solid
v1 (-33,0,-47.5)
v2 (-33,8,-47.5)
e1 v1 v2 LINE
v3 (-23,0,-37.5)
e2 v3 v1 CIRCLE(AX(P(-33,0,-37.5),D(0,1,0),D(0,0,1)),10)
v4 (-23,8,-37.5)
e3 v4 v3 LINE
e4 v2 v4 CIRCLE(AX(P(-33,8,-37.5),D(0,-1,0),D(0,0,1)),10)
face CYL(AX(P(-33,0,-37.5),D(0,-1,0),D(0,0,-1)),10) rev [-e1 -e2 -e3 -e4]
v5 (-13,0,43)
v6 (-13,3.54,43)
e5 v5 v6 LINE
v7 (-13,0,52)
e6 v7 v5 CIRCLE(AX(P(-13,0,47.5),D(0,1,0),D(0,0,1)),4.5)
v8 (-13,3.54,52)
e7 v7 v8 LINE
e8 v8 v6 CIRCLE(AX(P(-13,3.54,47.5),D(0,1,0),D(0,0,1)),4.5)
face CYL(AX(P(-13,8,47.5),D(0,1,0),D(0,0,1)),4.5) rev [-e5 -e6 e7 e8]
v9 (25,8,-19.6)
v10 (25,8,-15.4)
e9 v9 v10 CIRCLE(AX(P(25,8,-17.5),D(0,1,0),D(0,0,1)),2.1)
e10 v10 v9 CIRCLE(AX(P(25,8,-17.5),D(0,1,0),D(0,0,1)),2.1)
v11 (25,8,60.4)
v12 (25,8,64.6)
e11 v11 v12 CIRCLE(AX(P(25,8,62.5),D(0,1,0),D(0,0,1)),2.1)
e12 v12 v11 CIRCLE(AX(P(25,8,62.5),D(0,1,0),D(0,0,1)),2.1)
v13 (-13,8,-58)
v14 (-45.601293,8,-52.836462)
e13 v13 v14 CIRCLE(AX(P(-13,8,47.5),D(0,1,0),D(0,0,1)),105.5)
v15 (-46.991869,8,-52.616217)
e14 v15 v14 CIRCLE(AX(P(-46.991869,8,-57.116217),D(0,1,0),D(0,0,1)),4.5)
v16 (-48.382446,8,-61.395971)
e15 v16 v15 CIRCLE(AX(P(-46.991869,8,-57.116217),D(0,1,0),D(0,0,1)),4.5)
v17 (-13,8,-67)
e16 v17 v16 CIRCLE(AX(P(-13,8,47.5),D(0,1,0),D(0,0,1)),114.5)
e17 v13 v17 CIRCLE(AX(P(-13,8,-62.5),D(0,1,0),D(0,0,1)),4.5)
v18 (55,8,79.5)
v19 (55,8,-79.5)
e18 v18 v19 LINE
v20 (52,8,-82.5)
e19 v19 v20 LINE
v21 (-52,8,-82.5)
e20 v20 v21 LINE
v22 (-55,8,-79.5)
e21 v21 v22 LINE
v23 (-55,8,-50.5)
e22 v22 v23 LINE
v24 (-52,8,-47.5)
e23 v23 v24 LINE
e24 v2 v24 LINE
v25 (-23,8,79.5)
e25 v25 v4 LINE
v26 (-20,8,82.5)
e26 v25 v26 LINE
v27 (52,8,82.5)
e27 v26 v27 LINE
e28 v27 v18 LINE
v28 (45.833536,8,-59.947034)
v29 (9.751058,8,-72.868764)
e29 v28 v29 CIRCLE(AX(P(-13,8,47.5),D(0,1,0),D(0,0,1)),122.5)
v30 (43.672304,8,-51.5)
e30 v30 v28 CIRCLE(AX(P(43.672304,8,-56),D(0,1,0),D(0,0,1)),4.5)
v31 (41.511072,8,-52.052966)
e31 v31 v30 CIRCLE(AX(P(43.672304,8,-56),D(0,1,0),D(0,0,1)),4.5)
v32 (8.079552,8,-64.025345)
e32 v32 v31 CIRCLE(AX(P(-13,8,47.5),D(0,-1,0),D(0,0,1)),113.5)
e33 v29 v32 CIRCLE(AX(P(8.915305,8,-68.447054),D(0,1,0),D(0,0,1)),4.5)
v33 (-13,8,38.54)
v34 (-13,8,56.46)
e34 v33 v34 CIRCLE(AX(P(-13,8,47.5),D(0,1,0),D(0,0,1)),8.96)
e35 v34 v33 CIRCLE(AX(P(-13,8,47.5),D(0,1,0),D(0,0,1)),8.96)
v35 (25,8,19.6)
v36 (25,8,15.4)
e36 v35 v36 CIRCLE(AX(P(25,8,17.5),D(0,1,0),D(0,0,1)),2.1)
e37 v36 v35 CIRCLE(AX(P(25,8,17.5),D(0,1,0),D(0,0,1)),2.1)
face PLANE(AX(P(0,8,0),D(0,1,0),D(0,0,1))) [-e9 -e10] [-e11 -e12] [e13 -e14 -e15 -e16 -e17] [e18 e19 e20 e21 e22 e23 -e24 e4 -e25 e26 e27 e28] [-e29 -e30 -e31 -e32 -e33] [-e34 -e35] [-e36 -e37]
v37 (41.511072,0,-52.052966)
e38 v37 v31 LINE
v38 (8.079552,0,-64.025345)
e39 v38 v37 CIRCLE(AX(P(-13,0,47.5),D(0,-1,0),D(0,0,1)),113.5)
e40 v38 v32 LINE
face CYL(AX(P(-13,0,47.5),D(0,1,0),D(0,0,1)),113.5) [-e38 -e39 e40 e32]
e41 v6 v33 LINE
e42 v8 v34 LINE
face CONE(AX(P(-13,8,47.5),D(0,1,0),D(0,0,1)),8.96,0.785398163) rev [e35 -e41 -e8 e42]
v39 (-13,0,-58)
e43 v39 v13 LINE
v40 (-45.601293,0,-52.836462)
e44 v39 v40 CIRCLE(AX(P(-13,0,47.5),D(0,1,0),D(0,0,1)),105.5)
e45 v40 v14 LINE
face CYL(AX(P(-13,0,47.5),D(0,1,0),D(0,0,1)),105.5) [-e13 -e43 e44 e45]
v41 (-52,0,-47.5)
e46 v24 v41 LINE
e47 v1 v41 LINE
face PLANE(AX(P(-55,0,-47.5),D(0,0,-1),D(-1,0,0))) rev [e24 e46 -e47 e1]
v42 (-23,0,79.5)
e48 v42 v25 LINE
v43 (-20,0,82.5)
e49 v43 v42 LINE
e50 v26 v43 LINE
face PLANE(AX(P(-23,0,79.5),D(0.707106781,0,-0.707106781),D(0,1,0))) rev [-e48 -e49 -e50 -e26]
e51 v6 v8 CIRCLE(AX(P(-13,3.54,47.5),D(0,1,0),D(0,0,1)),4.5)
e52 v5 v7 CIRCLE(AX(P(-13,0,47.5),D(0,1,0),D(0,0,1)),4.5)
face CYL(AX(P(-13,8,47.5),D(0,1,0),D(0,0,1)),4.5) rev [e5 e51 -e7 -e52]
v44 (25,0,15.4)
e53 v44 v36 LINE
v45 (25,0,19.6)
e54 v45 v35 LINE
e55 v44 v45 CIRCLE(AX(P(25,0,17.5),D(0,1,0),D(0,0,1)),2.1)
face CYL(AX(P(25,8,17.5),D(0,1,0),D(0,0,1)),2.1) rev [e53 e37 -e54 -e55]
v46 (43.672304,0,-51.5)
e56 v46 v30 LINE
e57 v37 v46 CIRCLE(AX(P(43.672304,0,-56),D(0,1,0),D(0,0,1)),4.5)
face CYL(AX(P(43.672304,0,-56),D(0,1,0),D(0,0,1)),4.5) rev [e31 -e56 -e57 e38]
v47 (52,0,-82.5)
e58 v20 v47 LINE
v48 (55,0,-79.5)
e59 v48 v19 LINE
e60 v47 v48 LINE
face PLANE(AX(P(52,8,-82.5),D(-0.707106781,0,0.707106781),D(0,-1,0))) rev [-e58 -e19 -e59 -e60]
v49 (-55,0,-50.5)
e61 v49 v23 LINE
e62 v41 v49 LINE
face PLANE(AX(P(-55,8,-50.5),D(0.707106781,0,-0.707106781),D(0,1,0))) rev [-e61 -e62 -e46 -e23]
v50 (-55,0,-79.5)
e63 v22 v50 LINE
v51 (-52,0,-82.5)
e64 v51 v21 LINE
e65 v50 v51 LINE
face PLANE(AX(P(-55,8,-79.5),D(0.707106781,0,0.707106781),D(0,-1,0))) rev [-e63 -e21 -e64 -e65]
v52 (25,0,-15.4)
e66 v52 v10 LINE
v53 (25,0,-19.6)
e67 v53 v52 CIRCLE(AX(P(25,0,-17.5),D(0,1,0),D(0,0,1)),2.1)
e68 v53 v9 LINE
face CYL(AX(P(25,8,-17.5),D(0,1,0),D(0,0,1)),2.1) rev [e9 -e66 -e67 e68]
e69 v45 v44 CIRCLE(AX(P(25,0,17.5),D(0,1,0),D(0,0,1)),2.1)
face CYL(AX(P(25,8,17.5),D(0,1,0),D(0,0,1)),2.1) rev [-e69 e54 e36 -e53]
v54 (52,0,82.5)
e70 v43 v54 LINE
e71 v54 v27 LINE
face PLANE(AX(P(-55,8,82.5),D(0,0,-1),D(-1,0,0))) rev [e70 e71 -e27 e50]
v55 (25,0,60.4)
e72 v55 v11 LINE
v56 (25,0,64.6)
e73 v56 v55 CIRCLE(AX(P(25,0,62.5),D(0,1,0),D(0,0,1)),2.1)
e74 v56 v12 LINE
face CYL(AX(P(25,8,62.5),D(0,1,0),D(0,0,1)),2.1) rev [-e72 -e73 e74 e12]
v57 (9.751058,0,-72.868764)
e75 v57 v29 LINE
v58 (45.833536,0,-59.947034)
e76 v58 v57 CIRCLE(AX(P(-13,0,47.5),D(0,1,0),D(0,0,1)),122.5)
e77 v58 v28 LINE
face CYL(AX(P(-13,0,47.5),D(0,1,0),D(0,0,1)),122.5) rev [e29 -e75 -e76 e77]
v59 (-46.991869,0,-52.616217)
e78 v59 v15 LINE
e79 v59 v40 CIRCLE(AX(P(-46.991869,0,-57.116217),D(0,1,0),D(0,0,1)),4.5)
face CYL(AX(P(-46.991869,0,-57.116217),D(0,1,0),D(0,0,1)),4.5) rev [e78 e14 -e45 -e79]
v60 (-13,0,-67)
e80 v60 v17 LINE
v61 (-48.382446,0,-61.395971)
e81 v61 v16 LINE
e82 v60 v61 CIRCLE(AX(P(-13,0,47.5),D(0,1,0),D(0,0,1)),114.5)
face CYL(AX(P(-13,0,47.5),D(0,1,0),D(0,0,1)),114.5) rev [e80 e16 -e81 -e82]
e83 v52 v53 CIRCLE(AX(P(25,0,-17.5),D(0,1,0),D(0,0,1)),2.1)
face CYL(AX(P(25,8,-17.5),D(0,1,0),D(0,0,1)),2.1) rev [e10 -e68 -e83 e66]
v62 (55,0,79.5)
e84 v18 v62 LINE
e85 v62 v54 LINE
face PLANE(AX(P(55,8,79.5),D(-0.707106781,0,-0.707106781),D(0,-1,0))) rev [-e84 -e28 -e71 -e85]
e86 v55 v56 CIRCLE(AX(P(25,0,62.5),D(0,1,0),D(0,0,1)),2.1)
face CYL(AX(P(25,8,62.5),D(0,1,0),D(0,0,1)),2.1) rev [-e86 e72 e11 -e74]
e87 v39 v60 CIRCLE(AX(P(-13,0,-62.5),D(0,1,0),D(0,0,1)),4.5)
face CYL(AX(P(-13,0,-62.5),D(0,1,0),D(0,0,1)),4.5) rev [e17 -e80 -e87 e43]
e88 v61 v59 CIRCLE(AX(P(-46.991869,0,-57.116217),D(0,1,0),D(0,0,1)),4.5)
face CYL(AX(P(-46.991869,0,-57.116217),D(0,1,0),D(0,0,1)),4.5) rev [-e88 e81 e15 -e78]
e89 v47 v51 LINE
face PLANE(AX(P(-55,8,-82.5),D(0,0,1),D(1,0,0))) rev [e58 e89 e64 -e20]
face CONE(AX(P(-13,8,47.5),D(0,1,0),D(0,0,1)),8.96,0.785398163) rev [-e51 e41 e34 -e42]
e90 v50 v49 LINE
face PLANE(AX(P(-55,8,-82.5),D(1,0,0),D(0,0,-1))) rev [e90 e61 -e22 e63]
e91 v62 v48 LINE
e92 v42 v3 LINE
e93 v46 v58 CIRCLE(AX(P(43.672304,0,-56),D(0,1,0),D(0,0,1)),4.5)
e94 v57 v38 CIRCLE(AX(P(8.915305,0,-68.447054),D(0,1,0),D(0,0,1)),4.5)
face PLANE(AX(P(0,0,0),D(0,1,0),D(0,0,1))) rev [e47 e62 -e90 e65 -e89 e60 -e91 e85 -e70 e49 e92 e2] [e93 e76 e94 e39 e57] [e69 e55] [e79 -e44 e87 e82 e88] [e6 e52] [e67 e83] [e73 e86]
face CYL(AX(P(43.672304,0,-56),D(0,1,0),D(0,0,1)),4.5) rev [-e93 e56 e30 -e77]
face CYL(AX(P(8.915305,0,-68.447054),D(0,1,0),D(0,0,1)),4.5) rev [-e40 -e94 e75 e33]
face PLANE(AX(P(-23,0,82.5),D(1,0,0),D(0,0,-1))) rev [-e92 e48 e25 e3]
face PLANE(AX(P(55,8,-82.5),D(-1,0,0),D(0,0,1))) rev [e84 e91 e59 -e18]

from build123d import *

# Parameters (mm, degrees)
SKETCH_1_W                   = 110
SKETCH_1_H                   = 165
EXTRUDE_1_DEPTH              = 8
SKETCH_2_W                   = 32
SKETCH_2_H                   = 130
CUT_EXTRUDE_1_DEPTH          = 8
HOLE_WIZARD_M8_1_D           = 9
HOLE_WIZARD_M8_1_DEPTH       = 10
HOLE_WIZARD_M8_1_CSINK_D     = 17.92
HOLE_WIZARD_M8_1_CSINK_ANGLE = 90
HOLE_WIZARD_M8_1_TIP         = 2.703872786
CUT_EXTRUDE_2_DEPTH          = 8
CUT_EXTRUDE_3_DEPTH          = 8
CHAMFER_1_SIZE               = 3
HOLE_WIZARD_M5_1_D           = 4.2
FILLET_1_R                   = 10


with BuildPart() as part:
    # 草图1 → 凸台-拉伸1 (new body)
    with BuildSketch(Plane(origin=(0, 0, 0), x_dir=(1, 0, 0), z_dir=(0, 1, 0))):
        Rectangle(SKETCH_1_W, SKETCH_1_H)
    extrude(amount=EXTRUDE_1_DEPTH)

    # 草图2 → 切除-拉伸1 (cut)
    with BuildSketch(Plane(origin=(0, 8, 0), x_dir=(1, 0, 0), z_dir=(0, 1, 0))):
        with Locations((-39, -17.5)):
            Rectangle(SKETCH_2_W, SKETCH_2_H)
    extrude(amount=-CUT_EXTRUDE_1_DEPTH, mode=Mode.SUBTRACT)

    # M8 六角凹锥坑螺钉的锥形沉头孔1
    with Locations(Plane(origin=(0, 8, 0), x_dir=(1, 0, 0), z_dir=(0, 1, 0))):
        with Locations((-13, -47.5)):
            CounterSinkHole(HOLE_WIZARD_M8_1_D / 2, HOLE_WIZARD_M8_1_CSINK_D / 2, depth=HOLE_WIZARD_M8_1_DEPTH, counter_sink_angle=HOLE_WIZARD_M8_1_CSINK_ANGLE)
            with Locations((0, 0, -(HOLE_WIZARD_M8_1_DEPTH + HOLE_WIZARD_M8_1_TIP / 2))):  # 118° drill point
                Cone(0, HOLE_WIZARD_M8_1_D / 2, HOLE_WIZARD_M8_1_TIP, mode=Mode.SUBTRACT)

    # 草图6 → 切除-拉伸2 (cut)
    with BuildSketch(Plane(origin=(0, 8, 0), x_dir=(1, 0, 0), z_dir=(0, 1, 0))):
        with BuildLine():
            ThreePointArc((-13, 67), (-30.911746247, 65.590314998), (-48.382445856, 61.395971116))
            ThreePointArc((-48.382445856, 61.395971116), (-51.271623705, 55.725640318), (-45.601292907, 52.836462469))
            ThreePointArc((-45.601292907, 52.836462469), (-29.503836062, 56.701119933), (-13, 58))
            ThreePointArc((-13, 58), (-8.5, 62.5), (-13, 67))
        make_face()
    extrude(amount=-CUT_EXTRUDE_2_DEPTH, mode=Mode.SUBTRACT)

    # 草图6<3> → 切除-拉伸3 (cut)
    with BuildSketch(Plane(origin=(0, 8, 0), x_dir=(1, 0, 0), z_dir=(0, 1, 0))):
        with BuildLine():
            ThreePointArc((-13, 67), (-30.911746247, 65.590314998), (-48.382445856, 61.395971116))
            ThreePointArc((-48.382445856, 61.395971116), (-51.271623705, 55.725640318), (-45.601292907, 52.836462469))
            ThreePointArc((-45.601292907, 52.836462469), (-29.503836062, 56.701119933), (-13, 58))
            ThreePointArc((-13, 58), (-8.5, 62.5), (-13, 67))
        make_face()
        with BuildLine():
            ThreePointArc((45.83353556, 59.947033898), (28.30077784, 67.827775275), (9.751057901, 72.868764073))
            ThreePointArc((9.751057901, 72.868764073), (4.493595053, 69.282807519), (8.079551606, 64.025344671))
            ThreePointArc((8.079551606, 64.025344671), (25.266434979, 59.354714234), (41.511071723, 52.052966102))
            ThreePointArc((41.511071723, 52.052966102), (47.61933754, 53.838768081), (45.83353556, 59.947033898))
        make_face()
    extrude(amount=-CUT_EXTRUDE_3_DEPTH, mode=Mode.SUBTRACT)

    # 倒角1
    chamfer_1_edges = [part.edges().sort_by_distance(p)[0] for p in [
        (-55, 4, -47.5),
        (-23, 4, 82.5),
        (55, 4, 82.5),
        (-55, 4, -82.5),
        (55, 4, -82.5),
    ]]
    chamfer(chamfer_1_edges, length=CHAMFER_1_SIZE)

    # M5 螺纹孔1 (through all)
    with Locations(Plane(origin=(0, 8, 0), x_dir=(1, 0, 0), z_dir=(0, 1, 0))):
        with Locations((25, -62.5), (25, -17.5), (25, 17.5)):
            Hole(HOLE_WIZARD_M5_1_D / 2)

    # 圆角1
    fillet_1_edges = [part.edges().sort_by_distance(p)[0] for p in [
        (-23, 4, -47.5),
    ]]
    fillet(fillet_1_edges, radius=FILLET_1_R)


solid = part.part
